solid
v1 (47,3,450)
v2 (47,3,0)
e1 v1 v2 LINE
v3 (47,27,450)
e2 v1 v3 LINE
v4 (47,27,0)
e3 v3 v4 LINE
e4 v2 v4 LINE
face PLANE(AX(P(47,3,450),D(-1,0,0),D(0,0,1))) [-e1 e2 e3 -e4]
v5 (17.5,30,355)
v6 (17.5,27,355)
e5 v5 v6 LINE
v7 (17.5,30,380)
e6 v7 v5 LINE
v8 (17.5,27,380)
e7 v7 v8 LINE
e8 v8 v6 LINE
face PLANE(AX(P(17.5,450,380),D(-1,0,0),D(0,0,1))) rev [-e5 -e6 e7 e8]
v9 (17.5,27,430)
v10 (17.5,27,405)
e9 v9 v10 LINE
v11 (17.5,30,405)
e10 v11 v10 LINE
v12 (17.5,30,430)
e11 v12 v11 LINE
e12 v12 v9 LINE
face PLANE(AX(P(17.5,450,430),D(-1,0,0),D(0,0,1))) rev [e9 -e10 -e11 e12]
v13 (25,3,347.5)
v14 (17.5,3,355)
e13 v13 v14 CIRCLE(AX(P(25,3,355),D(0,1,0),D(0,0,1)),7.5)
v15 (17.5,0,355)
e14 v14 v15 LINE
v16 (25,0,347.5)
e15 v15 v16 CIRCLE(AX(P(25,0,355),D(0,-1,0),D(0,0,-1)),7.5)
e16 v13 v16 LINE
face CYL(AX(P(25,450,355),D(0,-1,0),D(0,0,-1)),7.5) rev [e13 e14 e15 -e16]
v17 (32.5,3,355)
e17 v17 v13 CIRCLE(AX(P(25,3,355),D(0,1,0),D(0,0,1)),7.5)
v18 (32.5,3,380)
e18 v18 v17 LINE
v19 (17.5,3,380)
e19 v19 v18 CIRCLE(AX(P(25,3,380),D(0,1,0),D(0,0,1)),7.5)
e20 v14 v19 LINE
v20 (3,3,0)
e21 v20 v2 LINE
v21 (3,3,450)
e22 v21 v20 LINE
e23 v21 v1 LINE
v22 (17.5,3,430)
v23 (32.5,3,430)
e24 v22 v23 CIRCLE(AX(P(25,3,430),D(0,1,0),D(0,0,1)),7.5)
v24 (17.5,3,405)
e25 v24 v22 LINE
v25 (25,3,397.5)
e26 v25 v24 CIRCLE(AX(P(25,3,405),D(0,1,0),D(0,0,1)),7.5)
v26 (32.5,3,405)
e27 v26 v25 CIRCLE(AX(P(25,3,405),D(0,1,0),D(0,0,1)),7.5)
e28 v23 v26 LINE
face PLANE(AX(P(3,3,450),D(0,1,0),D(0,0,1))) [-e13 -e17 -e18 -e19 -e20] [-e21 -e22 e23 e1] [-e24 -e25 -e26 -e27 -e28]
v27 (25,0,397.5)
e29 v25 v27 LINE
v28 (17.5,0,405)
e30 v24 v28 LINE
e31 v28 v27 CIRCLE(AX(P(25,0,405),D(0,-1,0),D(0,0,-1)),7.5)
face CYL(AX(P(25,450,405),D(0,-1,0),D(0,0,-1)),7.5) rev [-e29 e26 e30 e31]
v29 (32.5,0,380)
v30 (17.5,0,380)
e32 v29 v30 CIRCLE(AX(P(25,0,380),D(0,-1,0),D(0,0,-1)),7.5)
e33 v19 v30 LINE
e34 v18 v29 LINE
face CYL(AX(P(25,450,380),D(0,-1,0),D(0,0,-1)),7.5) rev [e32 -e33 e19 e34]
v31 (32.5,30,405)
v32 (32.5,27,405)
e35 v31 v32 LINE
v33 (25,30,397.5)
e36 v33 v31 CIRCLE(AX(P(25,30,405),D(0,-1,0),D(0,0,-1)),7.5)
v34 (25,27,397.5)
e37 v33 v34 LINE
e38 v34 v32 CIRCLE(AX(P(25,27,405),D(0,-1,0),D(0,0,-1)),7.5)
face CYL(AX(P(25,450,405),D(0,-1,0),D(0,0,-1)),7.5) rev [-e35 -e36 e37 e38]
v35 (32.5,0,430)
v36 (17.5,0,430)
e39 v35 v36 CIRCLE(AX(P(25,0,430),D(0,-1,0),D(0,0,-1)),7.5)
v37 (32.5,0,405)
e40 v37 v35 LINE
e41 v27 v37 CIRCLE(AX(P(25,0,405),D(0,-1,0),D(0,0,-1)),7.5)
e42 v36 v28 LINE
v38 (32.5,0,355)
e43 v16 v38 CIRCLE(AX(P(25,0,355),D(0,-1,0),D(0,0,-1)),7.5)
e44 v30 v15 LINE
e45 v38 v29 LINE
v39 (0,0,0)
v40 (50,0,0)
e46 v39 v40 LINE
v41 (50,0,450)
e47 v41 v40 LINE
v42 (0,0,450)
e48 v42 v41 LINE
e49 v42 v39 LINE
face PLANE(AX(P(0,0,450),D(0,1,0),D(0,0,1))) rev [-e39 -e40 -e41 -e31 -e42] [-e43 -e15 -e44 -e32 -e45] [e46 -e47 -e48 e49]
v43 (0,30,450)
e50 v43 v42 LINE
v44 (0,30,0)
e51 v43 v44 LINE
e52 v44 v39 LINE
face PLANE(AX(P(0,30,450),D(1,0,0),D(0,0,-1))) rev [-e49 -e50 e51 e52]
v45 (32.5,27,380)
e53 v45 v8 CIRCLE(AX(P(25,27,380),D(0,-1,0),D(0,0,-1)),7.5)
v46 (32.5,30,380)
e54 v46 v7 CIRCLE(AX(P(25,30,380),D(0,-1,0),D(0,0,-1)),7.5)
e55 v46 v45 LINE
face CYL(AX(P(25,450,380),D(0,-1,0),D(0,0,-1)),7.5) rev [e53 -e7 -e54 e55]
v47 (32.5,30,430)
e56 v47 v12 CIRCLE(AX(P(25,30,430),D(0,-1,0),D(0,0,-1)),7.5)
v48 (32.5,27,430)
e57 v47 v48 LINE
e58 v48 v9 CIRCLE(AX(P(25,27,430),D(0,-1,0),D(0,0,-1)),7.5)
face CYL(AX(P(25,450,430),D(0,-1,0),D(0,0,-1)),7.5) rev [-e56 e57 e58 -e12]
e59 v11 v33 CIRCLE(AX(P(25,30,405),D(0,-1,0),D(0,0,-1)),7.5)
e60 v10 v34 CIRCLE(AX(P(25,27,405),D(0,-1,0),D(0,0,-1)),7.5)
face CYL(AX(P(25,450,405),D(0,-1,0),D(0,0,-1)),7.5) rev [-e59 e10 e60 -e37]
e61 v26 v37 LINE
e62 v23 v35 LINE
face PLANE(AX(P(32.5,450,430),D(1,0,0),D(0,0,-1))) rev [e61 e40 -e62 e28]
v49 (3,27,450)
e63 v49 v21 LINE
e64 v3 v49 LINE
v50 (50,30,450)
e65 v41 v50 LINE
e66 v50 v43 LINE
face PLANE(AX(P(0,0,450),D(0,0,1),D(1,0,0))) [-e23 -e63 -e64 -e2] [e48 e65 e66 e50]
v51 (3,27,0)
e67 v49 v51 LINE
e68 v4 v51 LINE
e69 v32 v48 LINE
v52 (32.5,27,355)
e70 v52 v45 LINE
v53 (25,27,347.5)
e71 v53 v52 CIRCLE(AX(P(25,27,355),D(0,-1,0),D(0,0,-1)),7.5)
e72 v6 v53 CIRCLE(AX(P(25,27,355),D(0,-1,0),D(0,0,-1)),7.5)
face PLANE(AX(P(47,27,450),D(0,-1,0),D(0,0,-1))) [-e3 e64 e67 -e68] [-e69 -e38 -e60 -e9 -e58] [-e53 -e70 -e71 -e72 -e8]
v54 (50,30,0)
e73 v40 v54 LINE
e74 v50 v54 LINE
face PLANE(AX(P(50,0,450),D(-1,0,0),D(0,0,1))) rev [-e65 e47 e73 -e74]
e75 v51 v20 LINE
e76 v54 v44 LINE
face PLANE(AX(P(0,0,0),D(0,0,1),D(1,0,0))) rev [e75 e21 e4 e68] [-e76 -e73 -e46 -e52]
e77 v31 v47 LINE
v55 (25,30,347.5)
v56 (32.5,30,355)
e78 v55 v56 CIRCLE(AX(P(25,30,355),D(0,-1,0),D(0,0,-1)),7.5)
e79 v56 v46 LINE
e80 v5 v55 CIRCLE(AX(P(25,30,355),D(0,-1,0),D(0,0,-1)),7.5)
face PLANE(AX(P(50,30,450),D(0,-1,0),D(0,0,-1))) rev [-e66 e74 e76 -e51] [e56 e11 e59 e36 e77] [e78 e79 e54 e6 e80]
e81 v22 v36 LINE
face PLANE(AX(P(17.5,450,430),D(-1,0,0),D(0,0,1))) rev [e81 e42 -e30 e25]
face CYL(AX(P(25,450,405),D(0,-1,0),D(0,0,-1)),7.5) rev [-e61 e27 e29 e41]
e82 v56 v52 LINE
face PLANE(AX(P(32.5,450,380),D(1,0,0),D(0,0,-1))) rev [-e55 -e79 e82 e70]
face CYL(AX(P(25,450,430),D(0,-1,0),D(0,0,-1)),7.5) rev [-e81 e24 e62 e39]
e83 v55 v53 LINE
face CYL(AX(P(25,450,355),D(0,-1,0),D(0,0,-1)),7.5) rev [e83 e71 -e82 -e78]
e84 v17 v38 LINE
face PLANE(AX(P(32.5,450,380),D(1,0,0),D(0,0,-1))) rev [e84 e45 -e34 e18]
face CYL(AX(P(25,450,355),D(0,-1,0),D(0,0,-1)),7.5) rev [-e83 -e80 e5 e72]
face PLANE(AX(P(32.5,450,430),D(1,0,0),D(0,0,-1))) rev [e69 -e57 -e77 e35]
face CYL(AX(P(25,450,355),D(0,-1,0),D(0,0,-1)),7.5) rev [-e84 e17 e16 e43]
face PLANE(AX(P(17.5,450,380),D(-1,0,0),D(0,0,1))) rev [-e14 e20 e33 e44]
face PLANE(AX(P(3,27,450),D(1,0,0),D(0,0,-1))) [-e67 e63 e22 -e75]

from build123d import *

# Parameters (mm, degrees)
SKETCH_1_W          = 50
SKETCH_1_H          = 30
SKETCH_1_W_2        = 44
SKETCH_1_H_2        = 24
EXTRUDE_1_DEPTH     = 450
CUT_EXTRUDE_2_DEPTH = 450
CUT_EXTRUDE_3_DEPTH = 450


with BuildPart() as part:
    # 草图1 → 凸台-拉伸1 (new body)
    with BuildSketch(Plane.XY):
        with Locations((25, 15)):
            Rectangle(SKETCH_1_W, SKETCH_1_H)
        with Locations((25, 15)):
            Rectangle(SKETCH_1_W_2, SKETCH_1_H_2, mode=Mode.SUBTRACT)
    extrude(amount=EXTRUDE_1_DEPTH)

    # 草图2 → 切除-拉伸2 (cut)
    with BuildSketch(Plane.XZ):
        with BuildLine():
            Line((17.5, 430), (17.5, 405))
            ThreePointArc((17.5, 405), (25, 397.5), (32.5, 405))
            Line((32.5, 405), (32.5, 430))
            ThreePointArc((32.5, 430), (25, 437.5), (17.5, 430))
        make_face()
    extrude(amount=-CUT_EXTRUDE_2_DEPTH, mode=Mode.SUBTRACT)

    # 草图4 → 切除-拉伸3 (cut)
    with BuildSketch(Plane.XZ):
        with BuildLine():
            Line((17.5, 380), (17.5, 355))
            ThreePointArc((17.5, 355), (25, 347.5), (32.5, 355))
            Line((32.5, 355), (32.5, 380))
            ThreePointArc((32.5, 380), (25, 387.5), (17.5, 380))
        make_face()
    extrude(amount=-CUT_EXTRUDE_3_DEPTH, mode=Mode.SUBTRACT)


solid = part.part
